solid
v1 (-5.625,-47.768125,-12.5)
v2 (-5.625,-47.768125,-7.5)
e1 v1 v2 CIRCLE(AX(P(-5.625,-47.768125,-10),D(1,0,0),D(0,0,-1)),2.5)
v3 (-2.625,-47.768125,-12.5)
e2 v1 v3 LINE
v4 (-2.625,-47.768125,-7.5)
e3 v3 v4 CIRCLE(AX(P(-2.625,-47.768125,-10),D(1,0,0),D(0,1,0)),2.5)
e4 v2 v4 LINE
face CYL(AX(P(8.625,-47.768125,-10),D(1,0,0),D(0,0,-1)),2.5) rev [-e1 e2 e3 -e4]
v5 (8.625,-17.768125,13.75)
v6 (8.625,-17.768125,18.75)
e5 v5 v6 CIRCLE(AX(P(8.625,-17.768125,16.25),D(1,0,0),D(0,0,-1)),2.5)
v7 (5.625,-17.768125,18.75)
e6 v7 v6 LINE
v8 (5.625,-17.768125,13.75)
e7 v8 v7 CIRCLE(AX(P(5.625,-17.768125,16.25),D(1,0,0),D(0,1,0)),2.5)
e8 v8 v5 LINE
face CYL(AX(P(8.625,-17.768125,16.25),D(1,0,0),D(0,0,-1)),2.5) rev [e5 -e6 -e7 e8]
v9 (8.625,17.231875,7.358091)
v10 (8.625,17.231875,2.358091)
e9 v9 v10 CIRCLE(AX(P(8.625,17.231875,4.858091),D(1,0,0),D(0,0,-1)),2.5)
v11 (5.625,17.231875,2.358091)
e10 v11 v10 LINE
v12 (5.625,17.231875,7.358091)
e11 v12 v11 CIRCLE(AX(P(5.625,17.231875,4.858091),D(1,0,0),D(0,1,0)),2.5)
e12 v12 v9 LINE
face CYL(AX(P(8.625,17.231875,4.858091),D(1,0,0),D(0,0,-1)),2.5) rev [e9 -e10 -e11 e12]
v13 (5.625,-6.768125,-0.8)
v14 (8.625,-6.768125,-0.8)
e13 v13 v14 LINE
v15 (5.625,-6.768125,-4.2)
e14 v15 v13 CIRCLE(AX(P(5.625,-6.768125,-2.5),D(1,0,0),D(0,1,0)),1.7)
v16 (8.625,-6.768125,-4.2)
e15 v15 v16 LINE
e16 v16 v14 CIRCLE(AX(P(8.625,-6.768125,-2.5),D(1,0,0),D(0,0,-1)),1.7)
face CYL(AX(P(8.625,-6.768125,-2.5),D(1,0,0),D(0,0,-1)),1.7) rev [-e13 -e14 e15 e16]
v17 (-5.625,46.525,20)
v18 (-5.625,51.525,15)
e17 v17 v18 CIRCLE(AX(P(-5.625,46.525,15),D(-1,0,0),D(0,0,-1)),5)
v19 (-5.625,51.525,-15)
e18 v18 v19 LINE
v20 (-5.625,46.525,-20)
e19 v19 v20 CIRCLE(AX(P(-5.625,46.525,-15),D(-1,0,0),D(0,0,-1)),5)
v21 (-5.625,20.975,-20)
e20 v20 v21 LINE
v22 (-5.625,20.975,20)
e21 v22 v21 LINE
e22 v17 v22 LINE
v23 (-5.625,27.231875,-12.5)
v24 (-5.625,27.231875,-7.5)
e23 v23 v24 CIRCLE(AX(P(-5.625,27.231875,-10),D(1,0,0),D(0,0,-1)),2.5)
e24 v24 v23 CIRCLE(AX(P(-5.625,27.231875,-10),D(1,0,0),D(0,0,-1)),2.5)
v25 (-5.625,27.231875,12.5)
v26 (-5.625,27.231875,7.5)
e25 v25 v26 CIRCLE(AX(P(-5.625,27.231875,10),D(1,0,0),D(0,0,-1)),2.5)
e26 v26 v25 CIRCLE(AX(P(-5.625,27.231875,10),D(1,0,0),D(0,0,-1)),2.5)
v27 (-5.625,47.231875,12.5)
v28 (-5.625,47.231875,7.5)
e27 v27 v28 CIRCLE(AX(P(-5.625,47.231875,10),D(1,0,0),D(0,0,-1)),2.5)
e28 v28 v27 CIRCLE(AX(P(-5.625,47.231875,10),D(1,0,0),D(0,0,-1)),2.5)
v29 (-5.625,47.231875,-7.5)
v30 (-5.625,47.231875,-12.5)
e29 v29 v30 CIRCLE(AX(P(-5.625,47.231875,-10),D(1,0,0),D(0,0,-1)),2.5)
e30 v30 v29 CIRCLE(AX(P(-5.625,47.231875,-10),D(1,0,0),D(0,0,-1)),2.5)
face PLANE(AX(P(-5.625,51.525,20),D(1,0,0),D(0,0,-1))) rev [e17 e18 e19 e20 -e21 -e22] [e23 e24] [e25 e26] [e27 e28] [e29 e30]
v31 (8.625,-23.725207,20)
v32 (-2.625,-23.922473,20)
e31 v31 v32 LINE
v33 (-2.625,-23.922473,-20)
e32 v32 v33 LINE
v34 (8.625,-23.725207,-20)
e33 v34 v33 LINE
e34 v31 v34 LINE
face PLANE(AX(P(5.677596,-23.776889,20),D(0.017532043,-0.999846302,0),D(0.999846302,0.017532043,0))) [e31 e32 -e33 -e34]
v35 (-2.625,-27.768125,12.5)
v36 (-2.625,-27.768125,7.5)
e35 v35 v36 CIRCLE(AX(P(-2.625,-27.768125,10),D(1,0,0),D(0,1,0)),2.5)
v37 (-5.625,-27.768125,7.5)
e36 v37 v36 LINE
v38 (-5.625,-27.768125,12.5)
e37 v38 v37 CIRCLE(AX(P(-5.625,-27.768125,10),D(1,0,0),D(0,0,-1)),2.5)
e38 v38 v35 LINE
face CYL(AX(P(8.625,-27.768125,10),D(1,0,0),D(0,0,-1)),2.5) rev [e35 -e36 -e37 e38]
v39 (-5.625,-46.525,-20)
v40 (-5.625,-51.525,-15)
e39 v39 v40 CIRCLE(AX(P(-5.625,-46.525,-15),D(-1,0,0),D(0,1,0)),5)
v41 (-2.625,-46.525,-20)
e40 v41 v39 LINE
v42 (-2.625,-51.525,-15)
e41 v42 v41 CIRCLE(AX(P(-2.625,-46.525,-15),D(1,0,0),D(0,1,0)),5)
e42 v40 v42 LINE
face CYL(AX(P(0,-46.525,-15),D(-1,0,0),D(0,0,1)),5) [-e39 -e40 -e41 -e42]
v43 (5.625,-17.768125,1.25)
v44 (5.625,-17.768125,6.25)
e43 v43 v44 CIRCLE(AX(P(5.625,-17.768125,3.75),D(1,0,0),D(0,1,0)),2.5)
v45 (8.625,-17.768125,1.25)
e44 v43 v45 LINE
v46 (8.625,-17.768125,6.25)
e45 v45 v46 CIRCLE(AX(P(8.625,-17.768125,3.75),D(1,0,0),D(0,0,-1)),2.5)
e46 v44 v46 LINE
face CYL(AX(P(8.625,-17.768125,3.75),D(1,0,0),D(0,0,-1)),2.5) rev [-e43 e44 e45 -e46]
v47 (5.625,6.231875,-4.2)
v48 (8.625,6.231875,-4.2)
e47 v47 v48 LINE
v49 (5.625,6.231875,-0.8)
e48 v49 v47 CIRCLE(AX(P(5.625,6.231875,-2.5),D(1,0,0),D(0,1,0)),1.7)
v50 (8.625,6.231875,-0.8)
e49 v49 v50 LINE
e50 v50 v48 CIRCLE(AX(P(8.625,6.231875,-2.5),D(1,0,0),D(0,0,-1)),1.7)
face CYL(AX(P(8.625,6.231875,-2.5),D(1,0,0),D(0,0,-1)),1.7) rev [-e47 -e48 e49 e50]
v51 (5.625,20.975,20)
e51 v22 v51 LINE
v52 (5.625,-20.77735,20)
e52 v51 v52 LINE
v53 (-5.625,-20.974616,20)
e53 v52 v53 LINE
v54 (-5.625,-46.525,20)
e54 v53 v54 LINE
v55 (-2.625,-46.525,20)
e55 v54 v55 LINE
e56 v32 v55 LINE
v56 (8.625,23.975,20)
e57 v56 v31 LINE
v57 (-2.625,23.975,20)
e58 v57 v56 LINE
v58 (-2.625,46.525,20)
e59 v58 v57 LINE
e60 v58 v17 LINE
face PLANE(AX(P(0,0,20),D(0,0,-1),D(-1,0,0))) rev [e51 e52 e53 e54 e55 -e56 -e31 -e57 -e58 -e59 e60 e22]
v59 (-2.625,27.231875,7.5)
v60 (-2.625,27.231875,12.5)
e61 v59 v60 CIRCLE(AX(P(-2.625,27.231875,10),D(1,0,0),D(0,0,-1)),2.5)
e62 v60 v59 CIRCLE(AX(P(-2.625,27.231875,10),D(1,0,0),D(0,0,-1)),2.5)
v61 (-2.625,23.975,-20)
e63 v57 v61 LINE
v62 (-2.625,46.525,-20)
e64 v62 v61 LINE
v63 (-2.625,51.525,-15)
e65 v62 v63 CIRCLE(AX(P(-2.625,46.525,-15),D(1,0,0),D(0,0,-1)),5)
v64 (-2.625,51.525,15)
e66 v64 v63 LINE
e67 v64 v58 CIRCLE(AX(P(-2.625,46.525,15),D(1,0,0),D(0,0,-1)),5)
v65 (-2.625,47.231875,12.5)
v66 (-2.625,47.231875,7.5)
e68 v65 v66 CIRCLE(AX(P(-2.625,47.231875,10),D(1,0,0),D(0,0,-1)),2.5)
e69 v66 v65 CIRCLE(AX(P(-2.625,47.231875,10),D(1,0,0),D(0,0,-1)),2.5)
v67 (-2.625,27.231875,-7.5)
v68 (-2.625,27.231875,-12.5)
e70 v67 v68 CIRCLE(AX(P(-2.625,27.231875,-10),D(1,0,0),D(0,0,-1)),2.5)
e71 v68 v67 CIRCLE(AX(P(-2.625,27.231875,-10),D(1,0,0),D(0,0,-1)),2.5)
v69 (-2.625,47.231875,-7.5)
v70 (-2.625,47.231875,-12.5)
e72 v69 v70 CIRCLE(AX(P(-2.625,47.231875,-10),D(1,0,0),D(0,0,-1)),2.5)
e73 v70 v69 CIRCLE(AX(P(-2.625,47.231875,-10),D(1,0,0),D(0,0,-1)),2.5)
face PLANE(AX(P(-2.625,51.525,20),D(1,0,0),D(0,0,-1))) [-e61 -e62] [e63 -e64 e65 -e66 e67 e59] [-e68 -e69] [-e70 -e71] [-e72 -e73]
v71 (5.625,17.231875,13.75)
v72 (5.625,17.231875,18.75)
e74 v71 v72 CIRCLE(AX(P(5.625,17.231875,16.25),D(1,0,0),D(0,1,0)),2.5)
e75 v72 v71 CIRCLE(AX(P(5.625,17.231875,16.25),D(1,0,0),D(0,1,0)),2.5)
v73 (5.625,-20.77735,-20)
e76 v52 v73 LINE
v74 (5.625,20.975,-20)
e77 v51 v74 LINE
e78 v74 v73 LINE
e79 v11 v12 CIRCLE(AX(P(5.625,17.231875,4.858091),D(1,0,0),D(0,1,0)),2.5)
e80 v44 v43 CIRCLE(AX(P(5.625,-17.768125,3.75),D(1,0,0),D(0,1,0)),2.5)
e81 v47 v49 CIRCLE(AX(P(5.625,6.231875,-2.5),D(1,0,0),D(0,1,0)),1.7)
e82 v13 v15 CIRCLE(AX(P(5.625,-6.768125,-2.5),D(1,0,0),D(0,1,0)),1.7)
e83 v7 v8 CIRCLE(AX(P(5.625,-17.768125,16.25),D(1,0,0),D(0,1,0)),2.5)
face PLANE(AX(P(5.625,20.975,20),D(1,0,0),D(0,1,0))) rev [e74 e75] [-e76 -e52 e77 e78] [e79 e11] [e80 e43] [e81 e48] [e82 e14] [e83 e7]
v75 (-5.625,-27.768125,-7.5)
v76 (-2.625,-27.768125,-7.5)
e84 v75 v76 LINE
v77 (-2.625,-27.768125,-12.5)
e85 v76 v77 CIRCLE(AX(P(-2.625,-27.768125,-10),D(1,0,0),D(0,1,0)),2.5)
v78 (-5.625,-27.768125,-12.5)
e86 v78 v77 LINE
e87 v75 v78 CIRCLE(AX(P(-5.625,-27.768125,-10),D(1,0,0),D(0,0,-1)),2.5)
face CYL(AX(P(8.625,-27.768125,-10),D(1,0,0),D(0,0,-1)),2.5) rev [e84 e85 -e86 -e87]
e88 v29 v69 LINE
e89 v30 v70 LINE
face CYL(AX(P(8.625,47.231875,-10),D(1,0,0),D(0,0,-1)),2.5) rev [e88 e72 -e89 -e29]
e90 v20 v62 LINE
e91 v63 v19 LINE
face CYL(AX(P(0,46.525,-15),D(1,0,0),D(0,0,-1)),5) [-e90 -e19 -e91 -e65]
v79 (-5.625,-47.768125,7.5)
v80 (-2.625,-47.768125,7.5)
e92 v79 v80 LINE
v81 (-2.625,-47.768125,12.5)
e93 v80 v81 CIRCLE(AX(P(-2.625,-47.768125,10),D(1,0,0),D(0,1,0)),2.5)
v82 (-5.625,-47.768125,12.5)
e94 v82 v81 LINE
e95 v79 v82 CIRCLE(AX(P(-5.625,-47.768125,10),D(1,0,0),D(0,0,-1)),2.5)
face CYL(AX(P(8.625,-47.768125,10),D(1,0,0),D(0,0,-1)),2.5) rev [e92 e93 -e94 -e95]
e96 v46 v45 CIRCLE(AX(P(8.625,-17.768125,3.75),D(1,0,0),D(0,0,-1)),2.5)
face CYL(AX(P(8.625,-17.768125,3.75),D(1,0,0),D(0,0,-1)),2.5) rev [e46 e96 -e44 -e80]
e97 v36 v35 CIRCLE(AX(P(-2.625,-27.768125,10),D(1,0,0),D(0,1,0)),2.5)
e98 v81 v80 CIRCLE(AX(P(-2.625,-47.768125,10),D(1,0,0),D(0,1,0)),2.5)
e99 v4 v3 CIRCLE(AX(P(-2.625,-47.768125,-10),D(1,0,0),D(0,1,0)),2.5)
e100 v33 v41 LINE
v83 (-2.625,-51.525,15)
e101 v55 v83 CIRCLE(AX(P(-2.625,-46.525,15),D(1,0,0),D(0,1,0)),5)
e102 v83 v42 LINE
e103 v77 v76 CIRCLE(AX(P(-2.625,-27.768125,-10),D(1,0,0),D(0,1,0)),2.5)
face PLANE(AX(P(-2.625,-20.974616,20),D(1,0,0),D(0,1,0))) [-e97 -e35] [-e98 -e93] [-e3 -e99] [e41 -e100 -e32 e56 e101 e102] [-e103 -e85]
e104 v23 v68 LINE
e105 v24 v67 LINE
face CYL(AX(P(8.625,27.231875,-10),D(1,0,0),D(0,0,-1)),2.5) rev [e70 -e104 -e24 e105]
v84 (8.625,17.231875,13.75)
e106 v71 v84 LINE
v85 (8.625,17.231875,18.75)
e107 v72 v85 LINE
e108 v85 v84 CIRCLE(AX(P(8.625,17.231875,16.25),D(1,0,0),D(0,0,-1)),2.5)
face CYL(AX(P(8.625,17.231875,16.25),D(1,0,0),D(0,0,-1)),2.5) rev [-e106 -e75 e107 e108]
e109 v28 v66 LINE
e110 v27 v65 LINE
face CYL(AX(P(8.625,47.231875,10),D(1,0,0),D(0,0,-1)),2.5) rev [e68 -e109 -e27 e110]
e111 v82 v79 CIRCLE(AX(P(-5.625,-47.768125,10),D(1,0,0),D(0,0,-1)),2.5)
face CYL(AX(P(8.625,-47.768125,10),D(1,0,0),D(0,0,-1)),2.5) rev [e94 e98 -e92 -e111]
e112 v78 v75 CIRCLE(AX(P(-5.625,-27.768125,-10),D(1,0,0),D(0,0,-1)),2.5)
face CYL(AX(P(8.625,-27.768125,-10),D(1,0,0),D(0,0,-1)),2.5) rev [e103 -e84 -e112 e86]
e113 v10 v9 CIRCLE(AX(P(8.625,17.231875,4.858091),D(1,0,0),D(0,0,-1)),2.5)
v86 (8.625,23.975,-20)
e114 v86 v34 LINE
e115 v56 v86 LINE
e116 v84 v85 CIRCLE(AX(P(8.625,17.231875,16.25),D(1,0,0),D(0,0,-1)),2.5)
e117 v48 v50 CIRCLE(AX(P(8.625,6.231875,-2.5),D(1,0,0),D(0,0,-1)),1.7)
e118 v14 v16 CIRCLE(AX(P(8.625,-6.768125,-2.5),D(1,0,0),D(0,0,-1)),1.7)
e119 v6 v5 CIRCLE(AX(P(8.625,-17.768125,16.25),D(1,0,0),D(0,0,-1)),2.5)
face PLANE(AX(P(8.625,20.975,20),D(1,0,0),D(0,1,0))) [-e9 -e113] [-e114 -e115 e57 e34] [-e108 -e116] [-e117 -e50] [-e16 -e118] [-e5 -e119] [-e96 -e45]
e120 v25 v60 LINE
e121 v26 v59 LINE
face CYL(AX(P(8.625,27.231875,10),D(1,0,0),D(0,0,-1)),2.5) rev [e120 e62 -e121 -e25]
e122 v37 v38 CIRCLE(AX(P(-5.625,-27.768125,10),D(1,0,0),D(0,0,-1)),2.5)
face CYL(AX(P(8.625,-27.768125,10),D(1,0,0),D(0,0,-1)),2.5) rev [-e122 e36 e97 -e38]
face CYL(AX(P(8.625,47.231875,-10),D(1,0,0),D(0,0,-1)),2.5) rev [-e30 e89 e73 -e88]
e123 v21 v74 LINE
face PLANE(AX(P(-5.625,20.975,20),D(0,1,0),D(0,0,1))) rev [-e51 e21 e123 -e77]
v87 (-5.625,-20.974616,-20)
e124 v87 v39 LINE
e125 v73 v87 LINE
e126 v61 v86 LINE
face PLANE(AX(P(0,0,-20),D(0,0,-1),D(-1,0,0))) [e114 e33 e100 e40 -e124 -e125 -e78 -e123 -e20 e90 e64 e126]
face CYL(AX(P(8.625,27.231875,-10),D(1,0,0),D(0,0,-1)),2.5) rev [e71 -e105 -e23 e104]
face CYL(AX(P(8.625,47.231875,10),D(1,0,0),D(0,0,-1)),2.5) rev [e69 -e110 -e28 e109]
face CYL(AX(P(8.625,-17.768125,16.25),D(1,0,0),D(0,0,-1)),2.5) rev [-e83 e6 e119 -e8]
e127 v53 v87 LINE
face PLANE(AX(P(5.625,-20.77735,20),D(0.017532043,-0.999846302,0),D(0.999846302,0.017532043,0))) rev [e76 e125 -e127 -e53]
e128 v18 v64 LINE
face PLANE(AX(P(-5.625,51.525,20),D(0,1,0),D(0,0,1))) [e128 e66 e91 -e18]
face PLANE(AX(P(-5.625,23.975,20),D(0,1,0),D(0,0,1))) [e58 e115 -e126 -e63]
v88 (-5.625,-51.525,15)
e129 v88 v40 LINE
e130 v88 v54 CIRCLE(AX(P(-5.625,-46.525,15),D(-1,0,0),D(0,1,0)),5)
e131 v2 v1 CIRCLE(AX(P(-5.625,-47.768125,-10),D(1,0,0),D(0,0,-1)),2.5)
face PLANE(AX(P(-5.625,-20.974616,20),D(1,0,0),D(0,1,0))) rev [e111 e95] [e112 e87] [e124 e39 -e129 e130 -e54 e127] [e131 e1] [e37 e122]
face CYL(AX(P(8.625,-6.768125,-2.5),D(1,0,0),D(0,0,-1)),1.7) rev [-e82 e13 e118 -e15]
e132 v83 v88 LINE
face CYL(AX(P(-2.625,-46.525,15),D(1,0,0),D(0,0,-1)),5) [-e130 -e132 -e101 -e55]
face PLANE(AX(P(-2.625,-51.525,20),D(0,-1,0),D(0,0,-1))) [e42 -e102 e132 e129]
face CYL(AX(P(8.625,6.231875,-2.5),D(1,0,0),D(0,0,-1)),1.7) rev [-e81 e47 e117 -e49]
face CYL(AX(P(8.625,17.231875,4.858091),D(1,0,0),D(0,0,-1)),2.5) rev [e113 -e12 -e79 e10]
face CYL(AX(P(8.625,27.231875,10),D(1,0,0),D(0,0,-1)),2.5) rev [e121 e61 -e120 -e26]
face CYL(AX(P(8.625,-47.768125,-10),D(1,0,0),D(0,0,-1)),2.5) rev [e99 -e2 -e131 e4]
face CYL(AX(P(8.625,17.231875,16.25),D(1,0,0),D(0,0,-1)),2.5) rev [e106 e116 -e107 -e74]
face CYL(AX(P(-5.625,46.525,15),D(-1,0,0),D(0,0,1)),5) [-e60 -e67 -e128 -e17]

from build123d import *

# Parameters (mm, degrees)
EXTRUDE_THIN1_DEPTH   = 20
FILLET1_R             = 5
SIZE_MM_DOWEL_HOLE1_D = 5
M4_TAPPED_HOLE1_D     = 3.4


with BuildPart() as part:
    # Sketch1 → Extrude-Thin1 (new, symmetric)
    with BuildSketch(Plane.XY):
        Polygon((-5.625, 51.525), (-5.625, 20.975), (5.625, 20.975), (5.625, -20.777349891), (-5.625, -20.974615696), (-5.625, -51.525), (-2.625, -51.525), (-2.625, -23.922472646), (8.625, -23.725206841), (8.625, 23.975), (-2.625, 23.975), (-2.625, 51.525), align=None)
    extrude(amount=EXTRUDE_THIN1_DEPTH, both=True)

    # Fillet1
    fillet1_edges = [part.edges().sort_by_distance(p)[0] for p in [
        (-4.125, 51.525, -20),
        (-4.125, -51.525, -20),
        (-4.125, 51.525, 20),
        (-4.125, -51.525, 20),
    ]]
    fillet(fillet1_edges, radius=FILLET1_R)

    # Size mm Dowel Hole1 (through all)
    with Locations(Plane(origin=(8.625, 0, 0), x_dir=(0, 0, -1), z_dir=(1, 0, 0))):
        with Locations((-3.75, -17.768125), (-16.25, -17.768125), (-4.858090708, 17.231875), (-16.25, 17.231875), (10, 47.231875), (10, 27.231875), (-10, 27.231875), (-10, 47.231875), (10, -47.768125), (10, -27.768125), (-10, -27.768125), (-10, -47.768125)):
            Hole(SIZE_MM_DOWEL_HOLE1_D / 2)

    # M4 Tapped Hole1 (through all)
    with Locations(Plane(origin=(8.625, 0, 0), x_dir=(0, 0, -1), z_dir=(1, 0, 0))):
        with Locations((2.5, -6.768125), (2.5, 6.231875)):
            Hole(M4_TAPPED_HOLE1_D / 2)


solid = part.part
